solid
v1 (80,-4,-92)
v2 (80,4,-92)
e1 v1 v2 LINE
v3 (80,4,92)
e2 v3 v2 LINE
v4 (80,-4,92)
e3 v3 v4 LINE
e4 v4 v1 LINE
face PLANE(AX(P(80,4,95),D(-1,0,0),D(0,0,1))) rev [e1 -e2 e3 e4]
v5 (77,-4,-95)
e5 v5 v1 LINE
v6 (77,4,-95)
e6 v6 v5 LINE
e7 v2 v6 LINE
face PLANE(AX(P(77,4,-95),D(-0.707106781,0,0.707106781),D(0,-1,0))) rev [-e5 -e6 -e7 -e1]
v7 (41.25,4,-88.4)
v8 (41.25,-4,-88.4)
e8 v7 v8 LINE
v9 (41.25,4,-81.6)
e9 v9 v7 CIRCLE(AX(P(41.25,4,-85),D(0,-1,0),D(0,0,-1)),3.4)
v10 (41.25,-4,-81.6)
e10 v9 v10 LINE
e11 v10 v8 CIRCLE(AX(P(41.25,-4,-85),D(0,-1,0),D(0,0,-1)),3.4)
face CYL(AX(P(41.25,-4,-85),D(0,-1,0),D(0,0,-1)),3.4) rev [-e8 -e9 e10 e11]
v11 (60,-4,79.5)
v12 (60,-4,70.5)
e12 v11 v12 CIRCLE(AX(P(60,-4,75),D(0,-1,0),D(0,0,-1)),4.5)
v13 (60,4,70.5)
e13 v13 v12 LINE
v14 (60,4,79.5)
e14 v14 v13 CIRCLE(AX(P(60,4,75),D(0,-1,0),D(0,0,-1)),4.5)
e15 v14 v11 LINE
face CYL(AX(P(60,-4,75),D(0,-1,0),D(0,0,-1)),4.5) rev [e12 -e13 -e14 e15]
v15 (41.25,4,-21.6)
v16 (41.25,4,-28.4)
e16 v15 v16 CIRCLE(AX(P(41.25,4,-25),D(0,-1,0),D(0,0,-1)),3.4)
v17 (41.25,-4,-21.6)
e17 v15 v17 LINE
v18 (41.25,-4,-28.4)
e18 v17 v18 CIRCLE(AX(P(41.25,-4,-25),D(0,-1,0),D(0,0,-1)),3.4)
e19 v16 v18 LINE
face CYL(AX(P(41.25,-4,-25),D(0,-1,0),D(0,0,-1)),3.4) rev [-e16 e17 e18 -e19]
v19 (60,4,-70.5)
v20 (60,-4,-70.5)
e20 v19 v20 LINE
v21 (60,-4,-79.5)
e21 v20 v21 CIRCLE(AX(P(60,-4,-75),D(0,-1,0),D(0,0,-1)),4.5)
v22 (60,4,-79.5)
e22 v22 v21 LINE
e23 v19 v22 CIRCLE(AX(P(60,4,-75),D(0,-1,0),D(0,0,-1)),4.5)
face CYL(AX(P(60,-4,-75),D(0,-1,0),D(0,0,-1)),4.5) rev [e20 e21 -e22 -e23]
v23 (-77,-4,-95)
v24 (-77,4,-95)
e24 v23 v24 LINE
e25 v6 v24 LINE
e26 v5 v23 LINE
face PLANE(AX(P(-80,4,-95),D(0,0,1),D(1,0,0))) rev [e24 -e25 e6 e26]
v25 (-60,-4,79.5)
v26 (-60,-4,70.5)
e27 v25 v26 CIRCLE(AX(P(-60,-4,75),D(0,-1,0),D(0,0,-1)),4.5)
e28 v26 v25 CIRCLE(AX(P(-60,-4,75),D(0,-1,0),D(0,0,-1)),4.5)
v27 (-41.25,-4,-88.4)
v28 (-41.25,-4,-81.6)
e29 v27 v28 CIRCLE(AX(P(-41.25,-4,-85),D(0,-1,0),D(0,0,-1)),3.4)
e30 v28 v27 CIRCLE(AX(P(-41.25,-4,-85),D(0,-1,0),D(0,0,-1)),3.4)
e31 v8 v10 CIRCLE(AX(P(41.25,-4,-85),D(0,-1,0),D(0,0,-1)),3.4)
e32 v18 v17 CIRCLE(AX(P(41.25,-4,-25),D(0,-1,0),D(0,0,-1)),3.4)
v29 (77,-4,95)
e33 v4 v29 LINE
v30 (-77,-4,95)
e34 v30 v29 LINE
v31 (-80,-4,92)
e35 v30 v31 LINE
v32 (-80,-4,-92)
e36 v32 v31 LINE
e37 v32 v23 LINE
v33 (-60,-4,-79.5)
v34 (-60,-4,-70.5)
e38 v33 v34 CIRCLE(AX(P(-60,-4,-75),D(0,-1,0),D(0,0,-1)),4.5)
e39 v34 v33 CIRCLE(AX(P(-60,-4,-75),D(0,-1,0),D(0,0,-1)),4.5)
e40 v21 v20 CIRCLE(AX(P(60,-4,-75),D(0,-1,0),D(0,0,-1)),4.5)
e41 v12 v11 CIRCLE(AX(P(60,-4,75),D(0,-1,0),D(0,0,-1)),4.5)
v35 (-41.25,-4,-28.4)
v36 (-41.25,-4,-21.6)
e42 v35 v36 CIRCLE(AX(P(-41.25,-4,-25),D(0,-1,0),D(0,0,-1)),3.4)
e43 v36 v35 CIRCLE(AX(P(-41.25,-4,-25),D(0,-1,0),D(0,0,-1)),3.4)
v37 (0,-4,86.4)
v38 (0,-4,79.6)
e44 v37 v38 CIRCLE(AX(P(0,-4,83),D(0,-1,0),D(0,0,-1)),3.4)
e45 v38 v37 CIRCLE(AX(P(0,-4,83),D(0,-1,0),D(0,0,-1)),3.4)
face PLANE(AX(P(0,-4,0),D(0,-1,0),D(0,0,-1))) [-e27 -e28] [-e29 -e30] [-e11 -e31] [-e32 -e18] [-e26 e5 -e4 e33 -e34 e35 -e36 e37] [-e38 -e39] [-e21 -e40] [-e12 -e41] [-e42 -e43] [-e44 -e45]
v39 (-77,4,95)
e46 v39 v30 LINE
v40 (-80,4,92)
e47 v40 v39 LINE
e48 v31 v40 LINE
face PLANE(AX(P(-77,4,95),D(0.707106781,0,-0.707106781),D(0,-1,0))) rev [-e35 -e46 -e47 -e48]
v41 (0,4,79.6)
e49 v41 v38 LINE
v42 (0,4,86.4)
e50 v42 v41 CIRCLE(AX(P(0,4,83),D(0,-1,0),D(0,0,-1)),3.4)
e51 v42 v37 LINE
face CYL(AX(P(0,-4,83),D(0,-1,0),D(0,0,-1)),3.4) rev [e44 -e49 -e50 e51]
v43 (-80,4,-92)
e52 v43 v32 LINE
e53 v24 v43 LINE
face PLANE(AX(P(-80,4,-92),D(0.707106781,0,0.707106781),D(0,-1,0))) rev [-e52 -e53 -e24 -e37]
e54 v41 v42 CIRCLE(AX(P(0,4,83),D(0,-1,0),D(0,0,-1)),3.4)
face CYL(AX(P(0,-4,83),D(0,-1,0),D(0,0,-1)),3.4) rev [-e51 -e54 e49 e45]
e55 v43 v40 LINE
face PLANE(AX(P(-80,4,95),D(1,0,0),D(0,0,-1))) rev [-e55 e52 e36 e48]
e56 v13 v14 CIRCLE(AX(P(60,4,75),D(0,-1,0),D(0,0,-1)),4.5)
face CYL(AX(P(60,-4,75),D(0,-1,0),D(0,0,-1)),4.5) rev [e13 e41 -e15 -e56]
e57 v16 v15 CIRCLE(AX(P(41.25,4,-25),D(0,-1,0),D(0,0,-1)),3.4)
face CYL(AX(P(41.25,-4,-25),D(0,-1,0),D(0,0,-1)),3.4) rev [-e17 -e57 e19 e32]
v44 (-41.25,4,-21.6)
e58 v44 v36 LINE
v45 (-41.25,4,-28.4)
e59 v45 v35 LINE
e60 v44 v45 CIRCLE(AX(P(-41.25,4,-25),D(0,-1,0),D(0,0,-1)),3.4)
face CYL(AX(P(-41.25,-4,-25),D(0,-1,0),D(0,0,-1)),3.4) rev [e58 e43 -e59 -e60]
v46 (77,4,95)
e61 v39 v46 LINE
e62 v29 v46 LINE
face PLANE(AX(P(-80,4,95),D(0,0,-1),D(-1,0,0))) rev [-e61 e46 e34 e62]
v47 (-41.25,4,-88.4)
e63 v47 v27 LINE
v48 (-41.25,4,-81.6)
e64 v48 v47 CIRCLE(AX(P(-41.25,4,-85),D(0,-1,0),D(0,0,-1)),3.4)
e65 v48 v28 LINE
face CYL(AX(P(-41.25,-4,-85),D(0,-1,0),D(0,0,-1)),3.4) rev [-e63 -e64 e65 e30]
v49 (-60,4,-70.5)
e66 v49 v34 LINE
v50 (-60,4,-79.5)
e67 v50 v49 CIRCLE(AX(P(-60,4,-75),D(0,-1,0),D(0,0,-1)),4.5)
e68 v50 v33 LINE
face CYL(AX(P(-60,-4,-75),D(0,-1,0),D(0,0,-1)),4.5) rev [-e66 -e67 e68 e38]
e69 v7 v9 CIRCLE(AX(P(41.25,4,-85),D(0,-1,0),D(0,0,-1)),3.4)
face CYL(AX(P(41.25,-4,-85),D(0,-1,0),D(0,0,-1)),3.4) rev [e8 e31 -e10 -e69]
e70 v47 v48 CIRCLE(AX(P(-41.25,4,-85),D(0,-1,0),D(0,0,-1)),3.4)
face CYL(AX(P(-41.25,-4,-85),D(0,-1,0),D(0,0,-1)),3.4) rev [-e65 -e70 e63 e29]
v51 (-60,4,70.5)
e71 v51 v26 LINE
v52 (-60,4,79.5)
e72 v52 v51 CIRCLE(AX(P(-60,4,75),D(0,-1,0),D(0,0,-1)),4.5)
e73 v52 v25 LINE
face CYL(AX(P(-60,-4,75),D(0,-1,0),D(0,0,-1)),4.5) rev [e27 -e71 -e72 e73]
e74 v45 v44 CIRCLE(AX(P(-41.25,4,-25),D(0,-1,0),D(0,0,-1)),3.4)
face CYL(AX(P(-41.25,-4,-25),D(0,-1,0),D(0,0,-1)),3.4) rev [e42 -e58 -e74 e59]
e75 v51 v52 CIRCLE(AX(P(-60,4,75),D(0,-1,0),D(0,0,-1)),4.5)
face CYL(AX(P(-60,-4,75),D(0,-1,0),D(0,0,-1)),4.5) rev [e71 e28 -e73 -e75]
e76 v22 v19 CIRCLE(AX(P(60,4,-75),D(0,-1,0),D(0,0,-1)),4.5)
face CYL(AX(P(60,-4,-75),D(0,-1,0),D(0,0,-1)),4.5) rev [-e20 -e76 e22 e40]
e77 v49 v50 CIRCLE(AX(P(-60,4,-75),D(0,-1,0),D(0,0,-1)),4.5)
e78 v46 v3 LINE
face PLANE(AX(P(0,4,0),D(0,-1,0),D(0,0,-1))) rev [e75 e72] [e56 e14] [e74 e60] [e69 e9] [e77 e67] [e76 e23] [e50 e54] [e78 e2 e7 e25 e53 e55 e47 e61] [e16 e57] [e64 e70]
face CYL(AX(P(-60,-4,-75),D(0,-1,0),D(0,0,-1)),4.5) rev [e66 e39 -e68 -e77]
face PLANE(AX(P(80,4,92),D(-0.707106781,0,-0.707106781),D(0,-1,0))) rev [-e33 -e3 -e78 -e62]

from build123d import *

# Parameters (mm, degrees)
SKETCH_1_W            = 160
SKETCH_1_H            = 190
EXTRUDE_1_DEPTH       = 4
CHAMFER_1_SIZE        = 3
HOLE_WIZARD_9_0_9_1_D = 9
HOLE_WIZARD_M8_2_D    = 6.8
HOLE_WIZARD_M8_1_D    = 6.8


with BuildPart() as part:
    # 草图1 → 凸台-拉伸1 (new, symmetric)
    with BuildSketch(Plane(origin=(0, 0, 0), x_dir=(1, 0, 0), z_dir=(0, 1, 0))):
        Rectangle(SKETCH_1_W, SKETCH_1_H)
    extrude(amount=EXTRUDE_1_DEPTH, both=True)

    # 倒角1
    chamfer_1_edges = [part.edges().sort_by_distance(p)[0] for p in [
        (80, 0, 95),
        (-80, 0, 95),
        (-80, 0, -95),
        (80, 0, -95),
    ]]
    chamfer(chamfer_1_edges, length=CHAMFER_1_SIZE)

    # Ø9.0 (9) 直径孔1 (through all)
    with Locations(Plane(origin=(0, -4, 0), x_dir=(-1, 0, 0), z_dir=(0, -1, 0))):
        with Locations((-60, -75), (60, -75), (60, 75), (-60, 75)):
            Hole(HOLE_WIZARD_9_0_9_1_D / 2)

    # M8 螺纹孔2 (through all)
    with Locations(Plane(origin=(0, -4, 0), x_dir=(-1, 0, 0), z_dir=(0, -1, 0))):
        with Locations((-41.25, 25), (-41.25, 85), (41.25, 85), (41.25, 25)):
            Hole(HOLE_WIZARD_M8_2_D / 2)

    # M8 螺纹孔1 (through all)
    with Locations(Plane(origin=(0, -4, 0), x_dir=(-1, 0, 0), z_dir=(0, -1, 0))):
        with Locations((0, -83)):
            Hole(HOLE_WIZARD_M8_1_D / 2)


solid = part.part
